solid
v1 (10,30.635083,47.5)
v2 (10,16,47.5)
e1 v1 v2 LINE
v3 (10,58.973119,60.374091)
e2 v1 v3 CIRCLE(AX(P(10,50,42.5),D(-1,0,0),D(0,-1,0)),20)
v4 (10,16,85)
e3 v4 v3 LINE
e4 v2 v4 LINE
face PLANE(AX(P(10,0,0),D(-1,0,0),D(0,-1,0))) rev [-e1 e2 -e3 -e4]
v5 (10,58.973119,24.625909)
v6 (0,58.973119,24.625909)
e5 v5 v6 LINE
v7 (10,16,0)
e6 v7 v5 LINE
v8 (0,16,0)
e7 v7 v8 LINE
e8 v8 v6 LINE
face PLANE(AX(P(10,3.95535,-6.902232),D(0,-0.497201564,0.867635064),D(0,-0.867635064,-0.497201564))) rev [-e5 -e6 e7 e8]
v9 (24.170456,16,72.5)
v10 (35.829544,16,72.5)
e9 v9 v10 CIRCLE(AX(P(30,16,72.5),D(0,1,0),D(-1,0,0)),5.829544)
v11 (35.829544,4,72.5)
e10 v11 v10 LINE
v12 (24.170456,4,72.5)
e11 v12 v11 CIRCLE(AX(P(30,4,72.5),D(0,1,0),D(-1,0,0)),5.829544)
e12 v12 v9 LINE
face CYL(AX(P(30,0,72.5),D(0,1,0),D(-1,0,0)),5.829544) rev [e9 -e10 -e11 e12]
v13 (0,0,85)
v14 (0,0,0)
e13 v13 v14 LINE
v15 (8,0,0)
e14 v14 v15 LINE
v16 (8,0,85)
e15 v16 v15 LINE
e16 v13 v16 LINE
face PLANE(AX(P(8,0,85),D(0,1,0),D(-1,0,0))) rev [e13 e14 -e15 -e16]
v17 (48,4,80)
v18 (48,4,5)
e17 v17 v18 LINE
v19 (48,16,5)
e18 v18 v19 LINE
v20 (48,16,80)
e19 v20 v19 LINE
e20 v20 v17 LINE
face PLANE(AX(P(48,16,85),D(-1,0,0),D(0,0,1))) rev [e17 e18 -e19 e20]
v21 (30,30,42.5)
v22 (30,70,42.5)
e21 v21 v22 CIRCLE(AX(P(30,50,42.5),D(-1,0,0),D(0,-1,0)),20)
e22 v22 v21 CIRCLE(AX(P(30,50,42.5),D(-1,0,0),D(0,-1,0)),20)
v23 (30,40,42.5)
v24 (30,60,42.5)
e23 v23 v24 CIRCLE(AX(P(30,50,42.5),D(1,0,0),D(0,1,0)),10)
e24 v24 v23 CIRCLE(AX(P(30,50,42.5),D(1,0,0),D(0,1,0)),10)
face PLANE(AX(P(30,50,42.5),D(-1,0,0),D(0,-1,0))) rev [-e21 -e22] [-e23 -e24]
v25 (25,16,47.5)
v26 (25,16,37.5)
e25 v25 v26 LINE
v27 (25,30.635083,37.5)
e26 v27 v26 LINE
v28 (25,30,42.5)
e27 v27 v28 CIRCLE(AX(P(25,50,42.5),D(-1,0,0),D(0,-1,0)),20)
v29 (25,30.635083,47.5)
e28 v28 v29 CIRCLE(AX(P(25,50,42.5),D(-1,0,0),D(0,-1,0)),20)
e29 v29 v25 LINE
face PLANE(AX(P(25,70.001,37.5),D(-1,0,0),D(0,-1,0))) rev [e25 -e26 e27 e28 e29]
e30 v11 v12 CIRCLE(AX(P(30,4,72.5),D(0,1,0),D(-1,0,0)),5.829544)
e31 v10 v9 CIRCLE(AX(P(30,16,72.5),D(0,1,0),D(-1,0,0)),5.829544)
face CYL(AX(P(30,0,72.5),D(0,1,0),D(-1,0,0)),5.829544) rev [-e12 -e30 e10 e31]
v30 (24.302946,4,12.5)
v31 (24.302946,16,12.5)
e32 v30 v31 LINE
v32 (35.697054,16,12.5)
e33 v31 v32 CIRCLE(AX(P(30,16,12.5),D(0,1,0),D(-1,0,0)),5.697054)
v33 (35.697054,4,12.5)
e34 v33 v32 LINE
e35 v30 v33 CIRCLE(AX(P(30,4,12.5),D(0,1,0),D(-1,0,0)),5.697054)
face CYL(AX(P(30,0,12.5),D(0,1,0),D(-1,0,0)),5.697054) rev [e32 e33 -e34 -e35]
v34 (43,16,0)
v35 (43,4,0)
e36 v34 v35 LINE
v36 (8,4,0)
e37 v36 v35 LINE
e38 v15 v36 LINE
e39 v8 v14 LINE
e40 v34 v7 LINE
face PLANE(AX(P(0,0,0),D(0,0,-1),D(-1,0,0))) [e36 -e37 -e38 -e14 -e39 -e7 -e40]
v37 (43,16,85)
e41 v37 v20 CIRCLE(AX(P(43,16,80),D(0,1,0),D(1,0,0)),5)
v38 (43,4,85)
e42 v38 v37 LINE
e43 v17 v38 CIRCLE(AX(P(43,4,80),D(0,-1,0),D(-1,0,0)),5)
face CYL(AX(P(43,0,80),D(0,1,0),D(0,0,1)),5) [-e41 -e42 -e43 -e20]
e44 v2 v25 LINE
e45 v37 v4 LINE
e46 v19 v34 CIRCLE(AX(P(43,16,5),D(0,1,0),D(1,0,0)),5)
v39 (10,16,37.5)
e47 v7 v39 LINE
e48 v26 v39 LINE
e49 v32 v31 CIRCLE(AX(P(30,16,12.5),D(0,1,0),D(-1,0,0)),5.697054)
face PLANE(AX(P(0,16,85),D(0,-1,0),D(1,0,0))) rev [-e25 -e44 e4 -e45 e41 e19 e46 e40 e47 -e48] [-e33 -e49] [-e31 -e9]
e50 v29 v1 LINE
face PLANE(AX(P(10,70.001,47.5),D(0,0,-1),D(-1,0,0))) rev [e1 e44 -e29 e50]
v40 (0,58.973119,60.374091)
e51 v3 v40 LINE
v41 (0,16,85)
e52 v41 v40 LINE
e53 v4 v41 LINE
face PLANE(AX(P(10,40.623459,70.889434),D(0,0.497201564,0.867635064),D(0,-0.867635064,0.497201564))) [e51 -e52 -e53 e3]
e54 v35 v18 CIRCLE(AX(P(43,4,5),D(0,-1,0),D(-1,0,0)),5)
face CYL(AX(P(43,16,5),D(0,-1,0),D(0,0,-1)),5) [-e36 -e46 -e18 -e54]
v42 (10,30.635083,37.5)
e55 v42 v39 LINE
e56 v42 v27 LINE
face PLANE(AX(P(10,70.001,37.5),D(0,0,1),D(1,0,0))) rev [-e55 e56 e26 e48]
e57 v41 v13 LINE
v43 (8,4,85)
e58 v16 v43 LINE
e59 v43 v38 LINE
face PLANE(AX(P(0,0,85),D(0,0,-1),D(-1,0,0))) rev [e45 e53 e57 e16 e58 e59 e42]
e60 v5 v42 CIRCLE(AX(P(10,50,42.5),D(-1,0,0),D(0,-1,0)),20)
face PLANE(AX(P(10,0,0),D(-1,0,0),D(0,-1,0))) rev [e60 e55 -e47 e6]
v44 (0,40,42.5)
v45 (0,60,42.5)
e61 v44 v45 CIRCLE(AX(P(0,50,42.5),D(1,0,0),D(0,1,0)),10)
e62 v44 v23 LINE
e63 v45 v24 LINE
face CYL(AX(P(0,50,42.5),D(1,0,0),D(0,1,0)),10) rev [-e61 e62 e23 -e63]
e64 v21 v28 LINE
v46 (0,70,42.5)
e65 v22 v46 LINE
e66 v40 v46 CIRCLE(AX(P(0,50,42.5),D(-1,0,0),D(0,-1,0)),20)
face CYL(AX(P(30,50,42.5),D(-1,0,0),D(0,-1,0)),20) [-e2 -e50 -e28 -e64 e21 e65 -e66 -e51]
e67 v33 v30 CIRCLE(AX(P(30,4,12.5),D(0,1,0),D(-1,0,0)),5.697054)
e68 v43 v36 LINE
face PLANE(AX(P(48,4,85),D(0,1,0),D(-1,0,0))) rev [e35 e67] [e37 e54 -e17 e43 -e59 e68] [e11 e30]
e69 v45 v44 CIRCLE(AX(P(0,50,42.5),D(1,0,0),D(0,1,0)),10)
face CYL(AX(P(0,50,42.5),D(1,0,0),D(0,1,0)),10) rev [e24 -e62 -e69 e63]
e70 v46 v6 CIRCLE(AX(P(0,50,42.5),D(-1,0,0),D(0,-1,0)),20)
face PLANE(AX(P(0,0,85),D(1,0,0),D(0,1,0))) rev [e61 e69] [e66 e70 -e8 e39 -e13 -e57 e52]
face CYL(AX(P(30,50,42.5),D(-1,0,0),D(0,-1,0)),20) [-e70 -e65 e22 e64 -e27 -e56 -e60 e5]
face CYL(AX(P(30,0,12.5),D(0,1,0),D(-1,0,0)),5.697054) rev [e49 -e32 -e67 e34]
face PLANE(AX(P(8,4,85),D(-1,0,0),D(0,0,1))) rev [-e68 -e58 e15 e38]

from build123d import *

# Parameters (mm, degrees)
BASE_PLATE_DEPTH              = 85
PIVOT_BOSS_SKETCH_R           = 20
PIVOT_BOSS_DEPTH              = 30
GUSSET_RIB_DEPTH              = 10
BOSS_SUPPORT_BLOCK_REACH      = 113.557
BOSS_SUPPORT_BLOCK_END_RADIUS = 20
BOSS_SUPPORT_BLOCK_SKETCH_W   = 15
BOSS_SUPPORT_BLOCK_SKETCH_H   = 10
PIVOT_BORE_SKETCH_R           = 10
PIVOT_BORE_20_DEPTH           = 115.127122105
MOUNTING_HOLES_SKETCH_R       = 5.697054252
MOUNTING_HOLES_SKETCH_R_2     = 5.829543886
MOUNTING_HOLES_2X_DEPTH       = 112.557160236
CORNER_FILLETS_R5_R           = 5


with BuildPart() as part:
    # Base Plate Profile Sketch → Base Plate (new body)
    with BuildSketch(Plane.XY):
        Polygon((0, 0), (0, 16), (48, 16), (48, 4), (8, 4), (8, 0), align=None)
    extrude(amount=BASE_PLATE_DEPTH)



with BuildPart() as body_2:
    # Pivot Boss Sketch → Pivot Boss (new body)
    with BuildSketch(Plane.ZY):
        with Locations(Location((42.5, 50, 0), (0, 0, 270))):
            Circle(PIVOT_BOSS_SKETCH_R)
    extrude(amount=-PIVOT_BOSS_DEPTH)


with BuildPart() as part_1:
    add(part.part)

    add(body_2.part)  # Gusset Rib merges body 2
    # Gusset Rib Sketch → Gusset Rib (add)
    with BuildSketch(Plane.ZY):
        with BuildLine():
            Line((24.625908668, 58.973118691), (0, 16))
            Line((0, 16), (85, 16))
            Line((85, 16), (60.374091332, 58.973118691))
            ThreePointArc((60.374091332, 58.973118691), (61.961267002, 54.610757712), (62.5, 50))
            ThreePointArc((62.5, 50), (37.889242288, 30.538732998), (24.625908668, 58.973118691))
        make_face()
    extrude(amount=-GUSSET_RIB_DEPTH)

    # Boss Support Block: up to this cylinder (the profile starts outside it)
    boss_support_block_end = Plane(origin=(17.5, 50, 42.5), z_dir=(-1, 0, 0)) * Cylinder(BOSS_SUPPORT_BLOCK_END_RADIUS, 268.114, mode=Mode.PRIVATE)
    # Boss Support Block Sketch → Boss Support Block (add, up to the surface)
    with BuildSketch(Plane(origin=(0, 16, 0), x_dir=(1, 0, 0), z_dir=(0, 1, 0)), mode=Mode.PRIVATE) as boss_support_block_sk1:
        with Locations((17.5, -42.5)):
            Rectangle(BOSS_SUPPORT_BLOCK_SKETCH_W, BOSS_SUPPORT_BLOCK_SKETCH_H)
    boss_support_block_tool1 = extrude(boss_support_block_sk1.sketch, amount=BOSS_SUPPORT_BLOCK_REACH, mode=Mode.PRIVATE) - boss_support_block_end
    add(boss_support_block_tool1.solids().sort_by_distance((17.5, 16, 42.5))[0])

    # Pivot Bore Sketch → Pivot Bore Ø20 (cut, through all)
    with BuildSketch(Plane(origin=(30, 0, 0), x_dir=(0, 0, -1), z_dir=(1, 0, 0))):
        with Locations(Location((-42.5, 50, 0), (0, 0, 90))):
            Circle(PIVOT_BORE_SKETCH_R)
    extrude(amount=-PIVOT_BORE_20_DEPTH, mode=Mode.SUBTRACT)

    # Mounting Holes Sketch → Mounting Holes 2x (cut, through all)
    with BuildSketch(Plane(origin=(0, 16, 0), x_dir=(1, 0, 0), z_dir=(0, 1, 0))):
        with Locations(Location((30, -12.5, 0), (0, 0, 180))):
            Circle(MOUNTING_HOLES_SKETCH_R)
        with Locations(Location((30, -72.5, 0), (0, 0, 180))):
            Circle(MOUNTING_HOLES_SKETCH_R_2)
    extrude(amount=-MOUNTING_HOLES_2X_DEPTH, mode=Mode.SUBTRACT)

    # Corner Fillets R5
    corner_fillets_r5_edges = [part_1.edges().sort_by_distance(p)[0] for p in [
        (48, 10, 85),
        (48, 10, 0),
    ]]
    fillet(corner_fillets_r5_edges, radius=CORNER_FILLETS_R5_R)


solid = part_1.part
